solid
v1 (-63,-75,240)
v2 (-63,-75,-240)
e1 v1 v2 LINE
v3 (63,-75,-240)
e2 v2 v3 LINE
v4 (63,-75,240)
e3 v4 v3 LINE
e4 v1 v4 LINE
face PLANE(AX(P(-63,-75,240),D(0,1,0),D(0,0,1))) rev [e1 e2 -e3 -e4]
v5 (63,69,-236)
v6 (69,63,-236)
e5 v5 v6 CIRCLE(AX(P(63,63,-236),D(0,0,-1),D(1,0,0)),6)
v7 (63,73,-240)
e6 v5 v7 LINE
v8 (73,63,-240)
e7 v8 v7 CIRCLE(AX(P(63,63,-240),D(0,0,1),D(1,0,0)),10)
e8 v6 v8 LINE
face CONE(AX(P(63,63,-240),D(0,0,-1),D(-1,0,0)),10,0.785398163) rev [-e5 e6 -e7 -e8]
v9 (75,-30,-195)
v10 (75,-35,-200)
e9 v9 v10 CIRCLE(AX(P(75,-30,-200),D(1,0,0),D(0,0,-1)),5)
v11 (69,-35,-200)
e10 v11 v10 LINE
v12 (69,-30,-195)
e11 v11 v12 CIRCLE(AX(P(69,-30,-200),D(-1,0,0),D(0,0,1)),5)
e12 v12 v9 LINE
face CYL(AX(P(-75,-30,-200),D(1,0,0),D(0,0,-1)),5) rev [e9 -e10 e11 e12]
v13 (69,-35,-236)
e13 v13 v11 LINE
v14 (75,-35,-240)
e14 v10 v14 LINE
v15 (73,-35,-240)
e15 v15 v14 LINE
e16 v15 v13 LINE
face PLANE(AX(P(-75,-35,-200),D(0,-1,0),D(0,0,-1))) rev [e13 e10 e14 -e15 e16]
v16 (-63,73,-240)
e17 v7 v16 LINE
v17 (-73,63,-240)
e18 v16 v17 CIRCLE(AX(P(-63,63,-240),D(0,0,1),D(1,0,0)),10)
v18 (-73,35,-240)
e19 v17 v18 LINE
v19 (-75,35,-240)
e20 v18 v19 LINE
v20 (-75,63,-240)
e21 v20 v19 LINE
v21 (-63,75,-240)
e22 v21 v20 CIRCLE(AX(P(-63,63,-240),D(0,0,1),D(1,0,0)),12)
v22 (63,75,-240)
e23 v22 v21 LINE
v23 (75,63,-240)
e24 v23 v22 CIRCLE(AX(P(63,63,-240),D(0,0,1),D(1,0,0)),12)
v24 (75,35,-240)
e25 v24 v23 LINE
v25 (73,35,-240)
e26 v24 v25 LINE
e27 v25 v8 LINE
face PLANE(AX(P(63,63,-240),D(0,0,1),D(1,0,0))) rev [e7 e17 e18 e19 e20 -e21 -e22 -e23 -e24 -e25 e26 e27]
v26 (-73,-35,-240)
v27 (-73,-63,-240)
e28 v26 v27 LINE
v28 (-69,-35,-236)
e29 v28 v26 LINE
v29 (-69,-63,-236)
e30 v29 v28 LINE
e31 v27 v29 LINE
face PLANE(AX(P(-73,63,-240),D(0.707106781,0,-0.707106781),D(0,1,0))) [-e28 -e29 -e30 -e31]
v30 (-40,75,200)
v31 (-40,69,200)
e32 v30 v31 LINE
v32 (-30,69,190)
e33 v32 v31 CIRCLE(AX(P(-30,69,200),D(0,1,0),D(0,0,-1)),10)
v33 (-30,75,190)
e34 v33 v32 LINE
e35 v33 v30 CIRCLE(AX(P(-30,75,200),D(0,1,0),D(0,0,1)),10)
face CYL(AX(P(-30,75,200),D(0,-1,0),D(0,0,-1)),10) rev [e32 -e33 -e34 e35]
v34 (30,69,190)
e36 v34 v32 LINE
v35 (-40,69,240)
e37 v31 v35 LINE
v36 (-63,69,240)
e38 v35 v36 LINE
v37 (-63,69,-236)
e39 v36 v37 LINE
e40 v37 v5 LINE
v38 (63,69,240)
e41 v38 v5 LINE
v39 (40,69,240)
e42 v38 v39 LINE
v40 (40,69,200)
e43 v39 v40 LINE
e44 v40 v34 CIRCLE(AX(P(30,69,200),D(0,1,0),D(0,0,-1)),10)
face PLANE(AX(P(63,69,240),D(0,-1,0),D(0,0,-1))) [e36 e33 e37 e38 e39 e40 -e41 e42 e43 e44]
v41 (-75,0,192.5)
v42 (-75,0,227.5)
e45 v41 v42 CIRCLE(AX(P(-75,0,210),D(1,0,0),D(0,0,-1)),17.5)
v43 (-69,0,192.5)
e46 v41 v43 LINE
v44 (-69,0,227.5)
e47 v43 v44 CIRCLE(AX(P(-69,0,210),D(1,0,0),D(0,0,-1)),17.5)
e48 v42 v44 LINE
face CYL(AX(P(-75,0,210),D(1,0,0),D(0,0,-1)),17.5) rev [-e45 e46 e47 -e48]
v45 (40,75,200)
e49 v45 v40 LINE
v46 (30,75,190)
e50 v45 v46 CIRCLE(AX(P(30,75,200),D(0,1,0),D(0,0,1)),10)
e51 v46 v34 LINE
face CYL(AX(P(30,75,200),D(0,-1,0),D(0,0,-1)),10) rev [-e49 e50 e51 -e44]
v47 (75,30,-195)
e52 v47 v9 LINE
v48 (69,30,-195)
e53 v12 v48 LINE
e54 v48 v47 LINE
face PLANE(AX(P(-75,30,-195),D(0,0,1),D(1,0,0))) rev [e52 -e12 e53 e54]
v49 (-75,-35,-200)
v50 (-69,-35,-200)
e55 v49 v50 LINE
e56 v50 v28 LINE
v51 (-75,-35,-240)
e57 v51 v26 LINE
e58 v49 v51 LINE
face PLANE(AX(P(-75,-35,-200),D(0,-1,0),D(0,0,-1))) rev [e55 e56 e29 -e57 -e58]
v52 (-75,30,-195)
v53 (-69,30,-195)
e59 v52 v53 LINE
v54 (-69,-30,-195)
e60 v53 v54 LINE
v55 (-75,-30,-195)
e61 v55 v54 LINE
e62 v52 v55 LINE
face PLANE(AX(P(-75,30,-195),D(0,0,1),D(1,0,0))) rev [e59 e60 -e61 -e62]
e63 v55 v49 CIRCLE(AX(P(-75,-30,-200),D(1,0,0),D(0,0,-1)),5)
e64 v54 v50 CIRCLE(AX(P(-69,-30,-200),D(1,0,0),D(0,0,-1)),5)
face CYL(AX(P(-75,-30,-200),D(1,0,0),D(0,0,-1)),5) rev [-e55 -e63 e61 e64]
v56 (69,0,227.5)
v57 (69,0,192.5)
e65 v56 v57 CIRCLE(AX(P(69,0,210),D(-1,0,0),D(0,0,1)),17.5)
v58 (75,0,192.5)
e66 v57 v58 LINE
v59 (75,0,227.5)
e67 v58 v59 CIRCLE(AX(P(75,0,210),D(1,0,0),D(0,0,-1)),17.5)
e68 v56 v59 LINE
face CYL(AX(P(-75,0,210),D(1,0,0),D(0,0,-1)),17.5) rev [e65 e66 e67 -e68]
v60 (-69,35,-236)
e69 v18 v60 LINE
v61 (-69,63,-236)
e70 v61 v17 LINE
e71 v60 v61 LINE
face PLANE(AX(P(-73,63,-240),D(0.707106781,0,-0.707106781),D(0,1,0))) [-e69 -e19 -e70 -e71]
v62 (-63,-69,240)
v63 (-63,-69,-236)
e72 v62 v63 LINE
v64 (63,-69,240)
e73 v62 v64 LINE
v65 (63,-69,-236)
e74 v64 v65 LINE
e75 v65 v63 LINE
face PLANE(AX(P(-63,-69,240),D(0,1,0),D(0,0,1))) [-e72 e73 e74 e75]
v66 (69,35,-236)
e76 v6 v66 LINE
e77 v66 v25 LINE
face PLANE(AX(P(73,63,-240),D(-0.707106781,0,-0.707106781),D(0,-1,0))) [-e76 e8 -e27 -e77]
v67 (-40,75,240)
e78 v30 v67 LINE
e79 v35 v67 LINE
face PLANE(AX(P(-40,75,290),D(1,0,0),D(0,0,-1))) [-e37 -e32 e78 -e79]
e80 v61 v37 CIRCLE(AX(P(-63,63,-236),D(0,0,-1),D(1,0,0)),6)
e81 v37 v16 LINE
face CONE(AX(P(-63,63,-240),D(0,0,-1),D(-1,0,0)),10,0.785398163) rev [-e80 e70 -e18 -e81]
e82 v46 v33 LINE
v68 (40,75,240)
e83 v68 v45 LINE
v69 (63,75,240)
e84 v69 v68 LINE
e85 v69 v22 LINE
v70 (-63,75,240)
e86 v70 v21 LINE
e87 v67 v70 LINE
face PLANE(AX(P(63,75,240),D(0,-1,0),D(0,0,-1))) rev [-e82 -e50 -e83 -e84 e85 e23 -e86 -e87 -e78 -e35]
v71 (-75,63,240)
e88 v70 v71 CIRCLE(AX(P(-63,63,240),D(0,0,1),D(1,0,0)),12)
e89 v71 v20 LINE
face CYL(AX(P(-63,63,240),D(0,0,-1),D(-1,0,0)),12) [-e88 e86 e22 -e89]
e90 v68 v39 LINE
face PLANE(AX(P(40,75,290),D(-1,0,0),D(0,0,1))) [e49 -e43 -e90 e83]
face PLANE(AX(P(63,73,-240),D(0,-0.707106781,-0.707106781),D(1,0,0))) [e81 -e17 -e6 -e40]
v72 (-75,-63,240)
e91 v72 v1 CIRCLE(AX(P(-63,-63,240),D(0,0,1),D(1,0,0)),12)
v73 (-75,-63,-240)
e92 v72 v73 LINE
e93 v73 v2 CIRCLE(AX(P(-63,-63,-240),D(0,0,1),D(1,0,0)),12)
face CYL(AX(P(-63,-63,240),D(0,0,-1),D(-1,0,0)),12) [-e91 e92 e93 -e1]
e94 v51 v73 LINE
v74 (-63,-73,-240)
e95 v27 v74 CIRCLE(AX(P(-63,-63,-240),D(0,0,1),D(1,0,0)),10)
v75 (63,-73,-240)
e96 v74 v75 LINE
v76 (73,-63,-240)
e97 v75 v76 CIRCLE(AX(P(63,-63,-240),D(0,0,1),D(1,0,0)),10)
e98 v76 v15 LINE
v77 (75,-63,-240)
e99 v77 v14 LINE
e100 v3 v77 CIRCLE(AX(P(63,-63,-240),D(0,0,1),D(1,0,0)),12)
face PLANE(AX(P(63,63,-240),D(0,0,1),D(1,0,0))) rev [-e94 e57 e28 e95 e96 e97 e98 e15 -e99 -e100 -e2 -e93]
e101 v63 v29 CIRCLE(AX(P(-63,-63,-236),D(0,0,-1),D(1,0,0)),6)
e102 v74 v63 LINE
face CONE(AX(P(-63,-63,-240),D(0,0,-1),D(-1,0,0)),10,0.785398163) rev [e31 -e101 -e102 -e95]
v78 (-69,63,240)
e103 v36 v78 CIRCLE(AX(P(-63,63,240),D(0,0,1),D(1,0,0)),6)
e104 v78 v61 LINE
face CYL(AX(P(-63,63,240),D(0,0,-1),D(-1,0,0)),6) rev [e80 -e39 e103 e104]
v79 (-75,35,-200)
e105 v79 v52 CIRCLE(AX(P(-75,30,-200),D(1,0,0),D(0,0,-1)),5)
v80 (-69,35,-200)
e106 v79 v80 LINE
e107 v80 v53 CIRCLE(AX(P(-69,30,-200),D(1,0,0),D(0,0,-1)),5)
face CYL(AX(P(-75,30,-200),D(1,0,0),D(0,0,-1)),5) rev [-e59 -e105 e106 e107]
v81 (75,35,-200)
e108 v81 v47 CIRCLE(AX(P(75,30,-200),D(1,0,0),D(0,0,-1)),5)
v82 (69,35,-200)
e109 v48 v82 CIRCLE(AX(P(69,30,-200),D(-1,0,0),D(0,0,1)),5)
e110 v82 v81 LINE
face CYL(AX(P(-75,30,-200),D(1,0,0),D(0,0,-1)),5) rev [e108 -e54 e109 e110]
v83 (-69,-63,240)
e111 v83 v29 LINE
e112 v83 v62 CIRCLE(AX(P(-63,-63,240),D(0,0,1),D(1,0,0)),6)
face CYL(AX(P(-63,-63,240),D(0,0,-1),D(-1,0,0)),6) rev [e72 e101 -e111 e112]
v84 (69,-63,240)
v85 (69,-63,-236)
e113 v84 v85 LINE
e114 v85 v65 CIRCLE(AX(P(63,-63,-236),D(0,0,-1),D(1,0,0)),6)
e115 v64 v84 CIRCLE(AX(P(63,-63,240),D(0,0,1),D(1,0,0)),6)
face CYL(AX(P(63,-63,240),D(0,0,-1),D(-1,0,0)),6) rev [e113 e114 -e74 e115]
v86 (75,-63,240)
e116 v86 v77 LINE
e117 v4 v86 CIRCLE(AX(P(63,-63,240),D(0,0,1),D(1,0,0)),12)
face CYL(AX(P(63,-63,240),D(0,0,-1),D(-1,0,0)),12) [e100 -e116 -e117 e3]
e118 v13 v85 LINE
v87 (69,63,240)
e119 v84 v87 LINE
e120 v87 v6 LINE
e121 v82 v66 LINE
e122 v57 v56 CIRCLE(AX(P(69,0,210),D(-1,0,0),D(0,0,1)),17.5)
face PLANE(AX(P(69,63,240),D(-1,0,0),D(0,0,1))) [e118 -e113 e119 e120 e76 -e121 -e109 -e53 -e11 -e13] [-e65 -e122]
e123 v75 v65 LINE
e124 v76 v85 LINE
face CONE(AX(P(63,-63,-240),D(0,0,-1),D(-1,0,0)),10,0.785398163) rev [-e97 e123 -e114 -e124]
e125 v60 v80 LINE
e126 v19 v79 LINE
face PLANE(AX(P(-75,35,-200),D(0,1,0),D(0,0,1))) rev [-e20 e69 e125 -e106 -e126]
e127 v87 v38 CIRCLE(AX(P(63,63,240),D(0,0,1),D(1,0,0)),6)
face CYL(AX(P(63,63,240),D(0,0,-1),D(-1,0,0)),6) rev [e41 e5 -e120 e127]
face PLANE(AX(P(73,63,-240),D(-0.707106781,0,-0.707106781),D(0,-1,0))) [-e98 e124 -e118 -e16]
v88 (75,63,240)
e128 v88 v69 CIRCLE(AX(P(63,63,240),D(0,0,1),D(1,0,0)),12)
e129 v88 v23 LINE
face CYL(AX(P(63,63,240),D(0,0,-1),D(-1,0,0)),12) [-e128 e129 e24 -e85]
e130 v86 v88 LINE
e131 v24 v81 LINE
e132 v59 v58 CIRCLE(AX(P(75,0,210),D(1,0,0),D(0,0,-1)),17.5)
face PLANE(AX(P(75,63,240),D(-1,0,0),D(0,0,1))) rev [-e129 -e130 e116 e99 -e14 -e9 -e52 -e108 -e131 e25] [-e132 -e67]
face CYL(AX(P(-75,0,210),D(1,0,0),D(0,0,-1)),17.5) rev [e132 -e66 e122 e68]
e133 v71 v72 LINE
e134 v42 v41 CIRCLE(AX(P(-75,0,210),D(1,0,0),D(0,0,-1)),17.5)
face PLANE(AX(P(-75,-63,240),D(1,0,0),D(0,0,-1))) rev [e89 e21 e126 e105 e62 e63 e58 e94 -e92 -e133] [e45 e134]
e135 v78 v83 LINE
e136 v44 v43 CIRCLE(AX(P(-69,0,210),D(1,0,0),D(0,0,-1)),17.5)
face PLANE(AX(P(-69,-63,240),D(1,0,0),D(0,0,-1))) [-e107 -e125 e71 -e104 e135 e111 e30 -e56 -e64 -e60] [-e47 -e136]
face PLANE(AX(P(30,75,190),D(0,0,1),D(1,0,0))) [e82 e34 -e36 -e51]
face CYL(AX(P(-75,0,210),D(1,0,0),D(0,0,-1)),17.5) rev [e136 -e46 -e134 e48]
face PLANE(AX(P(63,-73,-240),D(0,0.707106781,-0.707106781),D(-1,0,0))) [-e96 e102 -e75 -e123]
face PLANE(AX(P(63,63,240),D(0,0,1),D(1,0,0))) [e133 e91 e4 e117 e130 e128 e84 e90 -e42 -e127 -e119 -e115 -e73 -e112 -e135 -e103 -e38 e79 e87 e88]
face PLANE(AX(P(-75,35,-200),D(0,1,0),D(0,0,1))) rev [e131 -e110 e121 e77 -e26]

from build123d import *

# Parameters (mm, degrees)
BOSS_EXTRUDE1_DEPTH     = 240
CUT_EXTRUDE1_DEPTH      = 263.392835268
CUT_EXTRUDE2_DEPTH      = 263.392835268
CUT_EXTRUDE2_DEPTH_BACK = 263.392835268
SKETCH2_R               = 17.5
CHAMFER1_SIZE           = 4


with BuildPart() as part:
    # Sketch1 → Boss-Extrude1 (new, symmetric)
    with BuildSketch(Plane.XY):
        with BuildLine():
            Line((-63, -75), (63, -75))
            ThreePointArc((63, -75), (71.485281374, -71.485281374), (75, -63))
            Line((75, -63), (75, 63))
            ThreePointArc((75, 63), (71.485281374, 71.485281374), (63, 75))
            Line((63, 75), (-63, 75))
            ThreePointArc((-63, 75), (-71.485281374, 71.485281374), (-75, 63))
            Line((-75, 63), (-75, -63))
            ThreePointArc((-75, -63), (-71.485281374, -71.485281374), (-63, -75))
        make_face()
        with BuildLine():
            Line((-63, -69), (63, -69))
            ThreePointArc((63, -69), (67.242640687, -67.242640687), (69, -63))
            Line((69, -63), (69, 63))
            ThreePointArc((69, 63), (67.242640687, 67.242640687), (63, 69))
            Line((63, 69), (-63, 69))
            ThreePointArc((-63, 69), (-67.242640687, 67.242640687), (-69, 63))
            Line((-69, 63), (-69, -63))
            ThreePointArc((-69, -63), (-67.242640687, -67.242640687), (-63, -69))
        make_face(mode=Mode.SUBTRACT)
    extrude(amount=BOSS_EXTRUDE1_DEPTH, both=True)

    # 草图1 → Cut-Extrude1 (cut, through all)
    with BuildSketch(Plane(origin=(0, 0, 0), x_dir=(1, 0, 0), z_dir=(0, 1, 0))):
        with BuildLine():
            Line((40, -290), (-40, -290))
            Line((-40, -290), (-40, -200))
            ThreePointArc((-40, -200), (-37.071067812, -192.928932188), (-30, -190))
            Line((-30, -190), (30, -190))
            ThreePointArc((30, -190), (37.071067812, -192.928932188), (40, -200))
            Line((40, -200), (40, -290))
        make_face()
    extrude(amount=CUT_EXTRUDE1_DEPTH, mode=Mode.SUBTRACT)

    # Sketch2 → Cut-Extrude2 (cut, two sides: drawn at the far end of the back side and taken through both)
    with BuildSketch(Plane(origin=(0, 0, 0), x_dir=(0, 0, -1), z_dir=(1, 0, 0)).offset(-CUT_EXTRUDE2_DEPTH_BACK)):
        with Locations((-210, 0)):
            Circle(SKETCH2_R)
        with BuildLine():
            Line((200, 35), (285, 35))
            Line((285, 35), (285, -35))
            Line((285, -35), (200, -35))
            ThreePointArc((200, -35), (196.464466094, -33.535533906), (195, -30))
            Line((195, -30), (195, 30))
            ThreePointArc((195, 30), (196.464466094, 33.535533906), (200, 35))
        make_face()
    extrude(amount=CUT_EXTRUDE2_DEPTH + CUT_EXTRUDE2_DEPTH_BACK, mode=Mode.SUBTRACT)

    # Chamfer1
    chamfer1_edges = [part.edges().sort_by_distance(p)[0] for p in [
        (-67.242640687, 67.242640687, -240),
        (-69, 49, -240),
        (-67.242640687, -67.242640687, -240),
        (0, -69, -240),
        (67.242640687, -67.242640687, -240),
        (69, -49, -240),
        (67.242640687, 67.242640687, -240),
        (0, 69, -240),
        (69, 49, -240),
        (-69, -49, -240),
    ]]
    chamfer(chamfer1_edges, length=CHAMFER1_SIZE)


solid = part.part
